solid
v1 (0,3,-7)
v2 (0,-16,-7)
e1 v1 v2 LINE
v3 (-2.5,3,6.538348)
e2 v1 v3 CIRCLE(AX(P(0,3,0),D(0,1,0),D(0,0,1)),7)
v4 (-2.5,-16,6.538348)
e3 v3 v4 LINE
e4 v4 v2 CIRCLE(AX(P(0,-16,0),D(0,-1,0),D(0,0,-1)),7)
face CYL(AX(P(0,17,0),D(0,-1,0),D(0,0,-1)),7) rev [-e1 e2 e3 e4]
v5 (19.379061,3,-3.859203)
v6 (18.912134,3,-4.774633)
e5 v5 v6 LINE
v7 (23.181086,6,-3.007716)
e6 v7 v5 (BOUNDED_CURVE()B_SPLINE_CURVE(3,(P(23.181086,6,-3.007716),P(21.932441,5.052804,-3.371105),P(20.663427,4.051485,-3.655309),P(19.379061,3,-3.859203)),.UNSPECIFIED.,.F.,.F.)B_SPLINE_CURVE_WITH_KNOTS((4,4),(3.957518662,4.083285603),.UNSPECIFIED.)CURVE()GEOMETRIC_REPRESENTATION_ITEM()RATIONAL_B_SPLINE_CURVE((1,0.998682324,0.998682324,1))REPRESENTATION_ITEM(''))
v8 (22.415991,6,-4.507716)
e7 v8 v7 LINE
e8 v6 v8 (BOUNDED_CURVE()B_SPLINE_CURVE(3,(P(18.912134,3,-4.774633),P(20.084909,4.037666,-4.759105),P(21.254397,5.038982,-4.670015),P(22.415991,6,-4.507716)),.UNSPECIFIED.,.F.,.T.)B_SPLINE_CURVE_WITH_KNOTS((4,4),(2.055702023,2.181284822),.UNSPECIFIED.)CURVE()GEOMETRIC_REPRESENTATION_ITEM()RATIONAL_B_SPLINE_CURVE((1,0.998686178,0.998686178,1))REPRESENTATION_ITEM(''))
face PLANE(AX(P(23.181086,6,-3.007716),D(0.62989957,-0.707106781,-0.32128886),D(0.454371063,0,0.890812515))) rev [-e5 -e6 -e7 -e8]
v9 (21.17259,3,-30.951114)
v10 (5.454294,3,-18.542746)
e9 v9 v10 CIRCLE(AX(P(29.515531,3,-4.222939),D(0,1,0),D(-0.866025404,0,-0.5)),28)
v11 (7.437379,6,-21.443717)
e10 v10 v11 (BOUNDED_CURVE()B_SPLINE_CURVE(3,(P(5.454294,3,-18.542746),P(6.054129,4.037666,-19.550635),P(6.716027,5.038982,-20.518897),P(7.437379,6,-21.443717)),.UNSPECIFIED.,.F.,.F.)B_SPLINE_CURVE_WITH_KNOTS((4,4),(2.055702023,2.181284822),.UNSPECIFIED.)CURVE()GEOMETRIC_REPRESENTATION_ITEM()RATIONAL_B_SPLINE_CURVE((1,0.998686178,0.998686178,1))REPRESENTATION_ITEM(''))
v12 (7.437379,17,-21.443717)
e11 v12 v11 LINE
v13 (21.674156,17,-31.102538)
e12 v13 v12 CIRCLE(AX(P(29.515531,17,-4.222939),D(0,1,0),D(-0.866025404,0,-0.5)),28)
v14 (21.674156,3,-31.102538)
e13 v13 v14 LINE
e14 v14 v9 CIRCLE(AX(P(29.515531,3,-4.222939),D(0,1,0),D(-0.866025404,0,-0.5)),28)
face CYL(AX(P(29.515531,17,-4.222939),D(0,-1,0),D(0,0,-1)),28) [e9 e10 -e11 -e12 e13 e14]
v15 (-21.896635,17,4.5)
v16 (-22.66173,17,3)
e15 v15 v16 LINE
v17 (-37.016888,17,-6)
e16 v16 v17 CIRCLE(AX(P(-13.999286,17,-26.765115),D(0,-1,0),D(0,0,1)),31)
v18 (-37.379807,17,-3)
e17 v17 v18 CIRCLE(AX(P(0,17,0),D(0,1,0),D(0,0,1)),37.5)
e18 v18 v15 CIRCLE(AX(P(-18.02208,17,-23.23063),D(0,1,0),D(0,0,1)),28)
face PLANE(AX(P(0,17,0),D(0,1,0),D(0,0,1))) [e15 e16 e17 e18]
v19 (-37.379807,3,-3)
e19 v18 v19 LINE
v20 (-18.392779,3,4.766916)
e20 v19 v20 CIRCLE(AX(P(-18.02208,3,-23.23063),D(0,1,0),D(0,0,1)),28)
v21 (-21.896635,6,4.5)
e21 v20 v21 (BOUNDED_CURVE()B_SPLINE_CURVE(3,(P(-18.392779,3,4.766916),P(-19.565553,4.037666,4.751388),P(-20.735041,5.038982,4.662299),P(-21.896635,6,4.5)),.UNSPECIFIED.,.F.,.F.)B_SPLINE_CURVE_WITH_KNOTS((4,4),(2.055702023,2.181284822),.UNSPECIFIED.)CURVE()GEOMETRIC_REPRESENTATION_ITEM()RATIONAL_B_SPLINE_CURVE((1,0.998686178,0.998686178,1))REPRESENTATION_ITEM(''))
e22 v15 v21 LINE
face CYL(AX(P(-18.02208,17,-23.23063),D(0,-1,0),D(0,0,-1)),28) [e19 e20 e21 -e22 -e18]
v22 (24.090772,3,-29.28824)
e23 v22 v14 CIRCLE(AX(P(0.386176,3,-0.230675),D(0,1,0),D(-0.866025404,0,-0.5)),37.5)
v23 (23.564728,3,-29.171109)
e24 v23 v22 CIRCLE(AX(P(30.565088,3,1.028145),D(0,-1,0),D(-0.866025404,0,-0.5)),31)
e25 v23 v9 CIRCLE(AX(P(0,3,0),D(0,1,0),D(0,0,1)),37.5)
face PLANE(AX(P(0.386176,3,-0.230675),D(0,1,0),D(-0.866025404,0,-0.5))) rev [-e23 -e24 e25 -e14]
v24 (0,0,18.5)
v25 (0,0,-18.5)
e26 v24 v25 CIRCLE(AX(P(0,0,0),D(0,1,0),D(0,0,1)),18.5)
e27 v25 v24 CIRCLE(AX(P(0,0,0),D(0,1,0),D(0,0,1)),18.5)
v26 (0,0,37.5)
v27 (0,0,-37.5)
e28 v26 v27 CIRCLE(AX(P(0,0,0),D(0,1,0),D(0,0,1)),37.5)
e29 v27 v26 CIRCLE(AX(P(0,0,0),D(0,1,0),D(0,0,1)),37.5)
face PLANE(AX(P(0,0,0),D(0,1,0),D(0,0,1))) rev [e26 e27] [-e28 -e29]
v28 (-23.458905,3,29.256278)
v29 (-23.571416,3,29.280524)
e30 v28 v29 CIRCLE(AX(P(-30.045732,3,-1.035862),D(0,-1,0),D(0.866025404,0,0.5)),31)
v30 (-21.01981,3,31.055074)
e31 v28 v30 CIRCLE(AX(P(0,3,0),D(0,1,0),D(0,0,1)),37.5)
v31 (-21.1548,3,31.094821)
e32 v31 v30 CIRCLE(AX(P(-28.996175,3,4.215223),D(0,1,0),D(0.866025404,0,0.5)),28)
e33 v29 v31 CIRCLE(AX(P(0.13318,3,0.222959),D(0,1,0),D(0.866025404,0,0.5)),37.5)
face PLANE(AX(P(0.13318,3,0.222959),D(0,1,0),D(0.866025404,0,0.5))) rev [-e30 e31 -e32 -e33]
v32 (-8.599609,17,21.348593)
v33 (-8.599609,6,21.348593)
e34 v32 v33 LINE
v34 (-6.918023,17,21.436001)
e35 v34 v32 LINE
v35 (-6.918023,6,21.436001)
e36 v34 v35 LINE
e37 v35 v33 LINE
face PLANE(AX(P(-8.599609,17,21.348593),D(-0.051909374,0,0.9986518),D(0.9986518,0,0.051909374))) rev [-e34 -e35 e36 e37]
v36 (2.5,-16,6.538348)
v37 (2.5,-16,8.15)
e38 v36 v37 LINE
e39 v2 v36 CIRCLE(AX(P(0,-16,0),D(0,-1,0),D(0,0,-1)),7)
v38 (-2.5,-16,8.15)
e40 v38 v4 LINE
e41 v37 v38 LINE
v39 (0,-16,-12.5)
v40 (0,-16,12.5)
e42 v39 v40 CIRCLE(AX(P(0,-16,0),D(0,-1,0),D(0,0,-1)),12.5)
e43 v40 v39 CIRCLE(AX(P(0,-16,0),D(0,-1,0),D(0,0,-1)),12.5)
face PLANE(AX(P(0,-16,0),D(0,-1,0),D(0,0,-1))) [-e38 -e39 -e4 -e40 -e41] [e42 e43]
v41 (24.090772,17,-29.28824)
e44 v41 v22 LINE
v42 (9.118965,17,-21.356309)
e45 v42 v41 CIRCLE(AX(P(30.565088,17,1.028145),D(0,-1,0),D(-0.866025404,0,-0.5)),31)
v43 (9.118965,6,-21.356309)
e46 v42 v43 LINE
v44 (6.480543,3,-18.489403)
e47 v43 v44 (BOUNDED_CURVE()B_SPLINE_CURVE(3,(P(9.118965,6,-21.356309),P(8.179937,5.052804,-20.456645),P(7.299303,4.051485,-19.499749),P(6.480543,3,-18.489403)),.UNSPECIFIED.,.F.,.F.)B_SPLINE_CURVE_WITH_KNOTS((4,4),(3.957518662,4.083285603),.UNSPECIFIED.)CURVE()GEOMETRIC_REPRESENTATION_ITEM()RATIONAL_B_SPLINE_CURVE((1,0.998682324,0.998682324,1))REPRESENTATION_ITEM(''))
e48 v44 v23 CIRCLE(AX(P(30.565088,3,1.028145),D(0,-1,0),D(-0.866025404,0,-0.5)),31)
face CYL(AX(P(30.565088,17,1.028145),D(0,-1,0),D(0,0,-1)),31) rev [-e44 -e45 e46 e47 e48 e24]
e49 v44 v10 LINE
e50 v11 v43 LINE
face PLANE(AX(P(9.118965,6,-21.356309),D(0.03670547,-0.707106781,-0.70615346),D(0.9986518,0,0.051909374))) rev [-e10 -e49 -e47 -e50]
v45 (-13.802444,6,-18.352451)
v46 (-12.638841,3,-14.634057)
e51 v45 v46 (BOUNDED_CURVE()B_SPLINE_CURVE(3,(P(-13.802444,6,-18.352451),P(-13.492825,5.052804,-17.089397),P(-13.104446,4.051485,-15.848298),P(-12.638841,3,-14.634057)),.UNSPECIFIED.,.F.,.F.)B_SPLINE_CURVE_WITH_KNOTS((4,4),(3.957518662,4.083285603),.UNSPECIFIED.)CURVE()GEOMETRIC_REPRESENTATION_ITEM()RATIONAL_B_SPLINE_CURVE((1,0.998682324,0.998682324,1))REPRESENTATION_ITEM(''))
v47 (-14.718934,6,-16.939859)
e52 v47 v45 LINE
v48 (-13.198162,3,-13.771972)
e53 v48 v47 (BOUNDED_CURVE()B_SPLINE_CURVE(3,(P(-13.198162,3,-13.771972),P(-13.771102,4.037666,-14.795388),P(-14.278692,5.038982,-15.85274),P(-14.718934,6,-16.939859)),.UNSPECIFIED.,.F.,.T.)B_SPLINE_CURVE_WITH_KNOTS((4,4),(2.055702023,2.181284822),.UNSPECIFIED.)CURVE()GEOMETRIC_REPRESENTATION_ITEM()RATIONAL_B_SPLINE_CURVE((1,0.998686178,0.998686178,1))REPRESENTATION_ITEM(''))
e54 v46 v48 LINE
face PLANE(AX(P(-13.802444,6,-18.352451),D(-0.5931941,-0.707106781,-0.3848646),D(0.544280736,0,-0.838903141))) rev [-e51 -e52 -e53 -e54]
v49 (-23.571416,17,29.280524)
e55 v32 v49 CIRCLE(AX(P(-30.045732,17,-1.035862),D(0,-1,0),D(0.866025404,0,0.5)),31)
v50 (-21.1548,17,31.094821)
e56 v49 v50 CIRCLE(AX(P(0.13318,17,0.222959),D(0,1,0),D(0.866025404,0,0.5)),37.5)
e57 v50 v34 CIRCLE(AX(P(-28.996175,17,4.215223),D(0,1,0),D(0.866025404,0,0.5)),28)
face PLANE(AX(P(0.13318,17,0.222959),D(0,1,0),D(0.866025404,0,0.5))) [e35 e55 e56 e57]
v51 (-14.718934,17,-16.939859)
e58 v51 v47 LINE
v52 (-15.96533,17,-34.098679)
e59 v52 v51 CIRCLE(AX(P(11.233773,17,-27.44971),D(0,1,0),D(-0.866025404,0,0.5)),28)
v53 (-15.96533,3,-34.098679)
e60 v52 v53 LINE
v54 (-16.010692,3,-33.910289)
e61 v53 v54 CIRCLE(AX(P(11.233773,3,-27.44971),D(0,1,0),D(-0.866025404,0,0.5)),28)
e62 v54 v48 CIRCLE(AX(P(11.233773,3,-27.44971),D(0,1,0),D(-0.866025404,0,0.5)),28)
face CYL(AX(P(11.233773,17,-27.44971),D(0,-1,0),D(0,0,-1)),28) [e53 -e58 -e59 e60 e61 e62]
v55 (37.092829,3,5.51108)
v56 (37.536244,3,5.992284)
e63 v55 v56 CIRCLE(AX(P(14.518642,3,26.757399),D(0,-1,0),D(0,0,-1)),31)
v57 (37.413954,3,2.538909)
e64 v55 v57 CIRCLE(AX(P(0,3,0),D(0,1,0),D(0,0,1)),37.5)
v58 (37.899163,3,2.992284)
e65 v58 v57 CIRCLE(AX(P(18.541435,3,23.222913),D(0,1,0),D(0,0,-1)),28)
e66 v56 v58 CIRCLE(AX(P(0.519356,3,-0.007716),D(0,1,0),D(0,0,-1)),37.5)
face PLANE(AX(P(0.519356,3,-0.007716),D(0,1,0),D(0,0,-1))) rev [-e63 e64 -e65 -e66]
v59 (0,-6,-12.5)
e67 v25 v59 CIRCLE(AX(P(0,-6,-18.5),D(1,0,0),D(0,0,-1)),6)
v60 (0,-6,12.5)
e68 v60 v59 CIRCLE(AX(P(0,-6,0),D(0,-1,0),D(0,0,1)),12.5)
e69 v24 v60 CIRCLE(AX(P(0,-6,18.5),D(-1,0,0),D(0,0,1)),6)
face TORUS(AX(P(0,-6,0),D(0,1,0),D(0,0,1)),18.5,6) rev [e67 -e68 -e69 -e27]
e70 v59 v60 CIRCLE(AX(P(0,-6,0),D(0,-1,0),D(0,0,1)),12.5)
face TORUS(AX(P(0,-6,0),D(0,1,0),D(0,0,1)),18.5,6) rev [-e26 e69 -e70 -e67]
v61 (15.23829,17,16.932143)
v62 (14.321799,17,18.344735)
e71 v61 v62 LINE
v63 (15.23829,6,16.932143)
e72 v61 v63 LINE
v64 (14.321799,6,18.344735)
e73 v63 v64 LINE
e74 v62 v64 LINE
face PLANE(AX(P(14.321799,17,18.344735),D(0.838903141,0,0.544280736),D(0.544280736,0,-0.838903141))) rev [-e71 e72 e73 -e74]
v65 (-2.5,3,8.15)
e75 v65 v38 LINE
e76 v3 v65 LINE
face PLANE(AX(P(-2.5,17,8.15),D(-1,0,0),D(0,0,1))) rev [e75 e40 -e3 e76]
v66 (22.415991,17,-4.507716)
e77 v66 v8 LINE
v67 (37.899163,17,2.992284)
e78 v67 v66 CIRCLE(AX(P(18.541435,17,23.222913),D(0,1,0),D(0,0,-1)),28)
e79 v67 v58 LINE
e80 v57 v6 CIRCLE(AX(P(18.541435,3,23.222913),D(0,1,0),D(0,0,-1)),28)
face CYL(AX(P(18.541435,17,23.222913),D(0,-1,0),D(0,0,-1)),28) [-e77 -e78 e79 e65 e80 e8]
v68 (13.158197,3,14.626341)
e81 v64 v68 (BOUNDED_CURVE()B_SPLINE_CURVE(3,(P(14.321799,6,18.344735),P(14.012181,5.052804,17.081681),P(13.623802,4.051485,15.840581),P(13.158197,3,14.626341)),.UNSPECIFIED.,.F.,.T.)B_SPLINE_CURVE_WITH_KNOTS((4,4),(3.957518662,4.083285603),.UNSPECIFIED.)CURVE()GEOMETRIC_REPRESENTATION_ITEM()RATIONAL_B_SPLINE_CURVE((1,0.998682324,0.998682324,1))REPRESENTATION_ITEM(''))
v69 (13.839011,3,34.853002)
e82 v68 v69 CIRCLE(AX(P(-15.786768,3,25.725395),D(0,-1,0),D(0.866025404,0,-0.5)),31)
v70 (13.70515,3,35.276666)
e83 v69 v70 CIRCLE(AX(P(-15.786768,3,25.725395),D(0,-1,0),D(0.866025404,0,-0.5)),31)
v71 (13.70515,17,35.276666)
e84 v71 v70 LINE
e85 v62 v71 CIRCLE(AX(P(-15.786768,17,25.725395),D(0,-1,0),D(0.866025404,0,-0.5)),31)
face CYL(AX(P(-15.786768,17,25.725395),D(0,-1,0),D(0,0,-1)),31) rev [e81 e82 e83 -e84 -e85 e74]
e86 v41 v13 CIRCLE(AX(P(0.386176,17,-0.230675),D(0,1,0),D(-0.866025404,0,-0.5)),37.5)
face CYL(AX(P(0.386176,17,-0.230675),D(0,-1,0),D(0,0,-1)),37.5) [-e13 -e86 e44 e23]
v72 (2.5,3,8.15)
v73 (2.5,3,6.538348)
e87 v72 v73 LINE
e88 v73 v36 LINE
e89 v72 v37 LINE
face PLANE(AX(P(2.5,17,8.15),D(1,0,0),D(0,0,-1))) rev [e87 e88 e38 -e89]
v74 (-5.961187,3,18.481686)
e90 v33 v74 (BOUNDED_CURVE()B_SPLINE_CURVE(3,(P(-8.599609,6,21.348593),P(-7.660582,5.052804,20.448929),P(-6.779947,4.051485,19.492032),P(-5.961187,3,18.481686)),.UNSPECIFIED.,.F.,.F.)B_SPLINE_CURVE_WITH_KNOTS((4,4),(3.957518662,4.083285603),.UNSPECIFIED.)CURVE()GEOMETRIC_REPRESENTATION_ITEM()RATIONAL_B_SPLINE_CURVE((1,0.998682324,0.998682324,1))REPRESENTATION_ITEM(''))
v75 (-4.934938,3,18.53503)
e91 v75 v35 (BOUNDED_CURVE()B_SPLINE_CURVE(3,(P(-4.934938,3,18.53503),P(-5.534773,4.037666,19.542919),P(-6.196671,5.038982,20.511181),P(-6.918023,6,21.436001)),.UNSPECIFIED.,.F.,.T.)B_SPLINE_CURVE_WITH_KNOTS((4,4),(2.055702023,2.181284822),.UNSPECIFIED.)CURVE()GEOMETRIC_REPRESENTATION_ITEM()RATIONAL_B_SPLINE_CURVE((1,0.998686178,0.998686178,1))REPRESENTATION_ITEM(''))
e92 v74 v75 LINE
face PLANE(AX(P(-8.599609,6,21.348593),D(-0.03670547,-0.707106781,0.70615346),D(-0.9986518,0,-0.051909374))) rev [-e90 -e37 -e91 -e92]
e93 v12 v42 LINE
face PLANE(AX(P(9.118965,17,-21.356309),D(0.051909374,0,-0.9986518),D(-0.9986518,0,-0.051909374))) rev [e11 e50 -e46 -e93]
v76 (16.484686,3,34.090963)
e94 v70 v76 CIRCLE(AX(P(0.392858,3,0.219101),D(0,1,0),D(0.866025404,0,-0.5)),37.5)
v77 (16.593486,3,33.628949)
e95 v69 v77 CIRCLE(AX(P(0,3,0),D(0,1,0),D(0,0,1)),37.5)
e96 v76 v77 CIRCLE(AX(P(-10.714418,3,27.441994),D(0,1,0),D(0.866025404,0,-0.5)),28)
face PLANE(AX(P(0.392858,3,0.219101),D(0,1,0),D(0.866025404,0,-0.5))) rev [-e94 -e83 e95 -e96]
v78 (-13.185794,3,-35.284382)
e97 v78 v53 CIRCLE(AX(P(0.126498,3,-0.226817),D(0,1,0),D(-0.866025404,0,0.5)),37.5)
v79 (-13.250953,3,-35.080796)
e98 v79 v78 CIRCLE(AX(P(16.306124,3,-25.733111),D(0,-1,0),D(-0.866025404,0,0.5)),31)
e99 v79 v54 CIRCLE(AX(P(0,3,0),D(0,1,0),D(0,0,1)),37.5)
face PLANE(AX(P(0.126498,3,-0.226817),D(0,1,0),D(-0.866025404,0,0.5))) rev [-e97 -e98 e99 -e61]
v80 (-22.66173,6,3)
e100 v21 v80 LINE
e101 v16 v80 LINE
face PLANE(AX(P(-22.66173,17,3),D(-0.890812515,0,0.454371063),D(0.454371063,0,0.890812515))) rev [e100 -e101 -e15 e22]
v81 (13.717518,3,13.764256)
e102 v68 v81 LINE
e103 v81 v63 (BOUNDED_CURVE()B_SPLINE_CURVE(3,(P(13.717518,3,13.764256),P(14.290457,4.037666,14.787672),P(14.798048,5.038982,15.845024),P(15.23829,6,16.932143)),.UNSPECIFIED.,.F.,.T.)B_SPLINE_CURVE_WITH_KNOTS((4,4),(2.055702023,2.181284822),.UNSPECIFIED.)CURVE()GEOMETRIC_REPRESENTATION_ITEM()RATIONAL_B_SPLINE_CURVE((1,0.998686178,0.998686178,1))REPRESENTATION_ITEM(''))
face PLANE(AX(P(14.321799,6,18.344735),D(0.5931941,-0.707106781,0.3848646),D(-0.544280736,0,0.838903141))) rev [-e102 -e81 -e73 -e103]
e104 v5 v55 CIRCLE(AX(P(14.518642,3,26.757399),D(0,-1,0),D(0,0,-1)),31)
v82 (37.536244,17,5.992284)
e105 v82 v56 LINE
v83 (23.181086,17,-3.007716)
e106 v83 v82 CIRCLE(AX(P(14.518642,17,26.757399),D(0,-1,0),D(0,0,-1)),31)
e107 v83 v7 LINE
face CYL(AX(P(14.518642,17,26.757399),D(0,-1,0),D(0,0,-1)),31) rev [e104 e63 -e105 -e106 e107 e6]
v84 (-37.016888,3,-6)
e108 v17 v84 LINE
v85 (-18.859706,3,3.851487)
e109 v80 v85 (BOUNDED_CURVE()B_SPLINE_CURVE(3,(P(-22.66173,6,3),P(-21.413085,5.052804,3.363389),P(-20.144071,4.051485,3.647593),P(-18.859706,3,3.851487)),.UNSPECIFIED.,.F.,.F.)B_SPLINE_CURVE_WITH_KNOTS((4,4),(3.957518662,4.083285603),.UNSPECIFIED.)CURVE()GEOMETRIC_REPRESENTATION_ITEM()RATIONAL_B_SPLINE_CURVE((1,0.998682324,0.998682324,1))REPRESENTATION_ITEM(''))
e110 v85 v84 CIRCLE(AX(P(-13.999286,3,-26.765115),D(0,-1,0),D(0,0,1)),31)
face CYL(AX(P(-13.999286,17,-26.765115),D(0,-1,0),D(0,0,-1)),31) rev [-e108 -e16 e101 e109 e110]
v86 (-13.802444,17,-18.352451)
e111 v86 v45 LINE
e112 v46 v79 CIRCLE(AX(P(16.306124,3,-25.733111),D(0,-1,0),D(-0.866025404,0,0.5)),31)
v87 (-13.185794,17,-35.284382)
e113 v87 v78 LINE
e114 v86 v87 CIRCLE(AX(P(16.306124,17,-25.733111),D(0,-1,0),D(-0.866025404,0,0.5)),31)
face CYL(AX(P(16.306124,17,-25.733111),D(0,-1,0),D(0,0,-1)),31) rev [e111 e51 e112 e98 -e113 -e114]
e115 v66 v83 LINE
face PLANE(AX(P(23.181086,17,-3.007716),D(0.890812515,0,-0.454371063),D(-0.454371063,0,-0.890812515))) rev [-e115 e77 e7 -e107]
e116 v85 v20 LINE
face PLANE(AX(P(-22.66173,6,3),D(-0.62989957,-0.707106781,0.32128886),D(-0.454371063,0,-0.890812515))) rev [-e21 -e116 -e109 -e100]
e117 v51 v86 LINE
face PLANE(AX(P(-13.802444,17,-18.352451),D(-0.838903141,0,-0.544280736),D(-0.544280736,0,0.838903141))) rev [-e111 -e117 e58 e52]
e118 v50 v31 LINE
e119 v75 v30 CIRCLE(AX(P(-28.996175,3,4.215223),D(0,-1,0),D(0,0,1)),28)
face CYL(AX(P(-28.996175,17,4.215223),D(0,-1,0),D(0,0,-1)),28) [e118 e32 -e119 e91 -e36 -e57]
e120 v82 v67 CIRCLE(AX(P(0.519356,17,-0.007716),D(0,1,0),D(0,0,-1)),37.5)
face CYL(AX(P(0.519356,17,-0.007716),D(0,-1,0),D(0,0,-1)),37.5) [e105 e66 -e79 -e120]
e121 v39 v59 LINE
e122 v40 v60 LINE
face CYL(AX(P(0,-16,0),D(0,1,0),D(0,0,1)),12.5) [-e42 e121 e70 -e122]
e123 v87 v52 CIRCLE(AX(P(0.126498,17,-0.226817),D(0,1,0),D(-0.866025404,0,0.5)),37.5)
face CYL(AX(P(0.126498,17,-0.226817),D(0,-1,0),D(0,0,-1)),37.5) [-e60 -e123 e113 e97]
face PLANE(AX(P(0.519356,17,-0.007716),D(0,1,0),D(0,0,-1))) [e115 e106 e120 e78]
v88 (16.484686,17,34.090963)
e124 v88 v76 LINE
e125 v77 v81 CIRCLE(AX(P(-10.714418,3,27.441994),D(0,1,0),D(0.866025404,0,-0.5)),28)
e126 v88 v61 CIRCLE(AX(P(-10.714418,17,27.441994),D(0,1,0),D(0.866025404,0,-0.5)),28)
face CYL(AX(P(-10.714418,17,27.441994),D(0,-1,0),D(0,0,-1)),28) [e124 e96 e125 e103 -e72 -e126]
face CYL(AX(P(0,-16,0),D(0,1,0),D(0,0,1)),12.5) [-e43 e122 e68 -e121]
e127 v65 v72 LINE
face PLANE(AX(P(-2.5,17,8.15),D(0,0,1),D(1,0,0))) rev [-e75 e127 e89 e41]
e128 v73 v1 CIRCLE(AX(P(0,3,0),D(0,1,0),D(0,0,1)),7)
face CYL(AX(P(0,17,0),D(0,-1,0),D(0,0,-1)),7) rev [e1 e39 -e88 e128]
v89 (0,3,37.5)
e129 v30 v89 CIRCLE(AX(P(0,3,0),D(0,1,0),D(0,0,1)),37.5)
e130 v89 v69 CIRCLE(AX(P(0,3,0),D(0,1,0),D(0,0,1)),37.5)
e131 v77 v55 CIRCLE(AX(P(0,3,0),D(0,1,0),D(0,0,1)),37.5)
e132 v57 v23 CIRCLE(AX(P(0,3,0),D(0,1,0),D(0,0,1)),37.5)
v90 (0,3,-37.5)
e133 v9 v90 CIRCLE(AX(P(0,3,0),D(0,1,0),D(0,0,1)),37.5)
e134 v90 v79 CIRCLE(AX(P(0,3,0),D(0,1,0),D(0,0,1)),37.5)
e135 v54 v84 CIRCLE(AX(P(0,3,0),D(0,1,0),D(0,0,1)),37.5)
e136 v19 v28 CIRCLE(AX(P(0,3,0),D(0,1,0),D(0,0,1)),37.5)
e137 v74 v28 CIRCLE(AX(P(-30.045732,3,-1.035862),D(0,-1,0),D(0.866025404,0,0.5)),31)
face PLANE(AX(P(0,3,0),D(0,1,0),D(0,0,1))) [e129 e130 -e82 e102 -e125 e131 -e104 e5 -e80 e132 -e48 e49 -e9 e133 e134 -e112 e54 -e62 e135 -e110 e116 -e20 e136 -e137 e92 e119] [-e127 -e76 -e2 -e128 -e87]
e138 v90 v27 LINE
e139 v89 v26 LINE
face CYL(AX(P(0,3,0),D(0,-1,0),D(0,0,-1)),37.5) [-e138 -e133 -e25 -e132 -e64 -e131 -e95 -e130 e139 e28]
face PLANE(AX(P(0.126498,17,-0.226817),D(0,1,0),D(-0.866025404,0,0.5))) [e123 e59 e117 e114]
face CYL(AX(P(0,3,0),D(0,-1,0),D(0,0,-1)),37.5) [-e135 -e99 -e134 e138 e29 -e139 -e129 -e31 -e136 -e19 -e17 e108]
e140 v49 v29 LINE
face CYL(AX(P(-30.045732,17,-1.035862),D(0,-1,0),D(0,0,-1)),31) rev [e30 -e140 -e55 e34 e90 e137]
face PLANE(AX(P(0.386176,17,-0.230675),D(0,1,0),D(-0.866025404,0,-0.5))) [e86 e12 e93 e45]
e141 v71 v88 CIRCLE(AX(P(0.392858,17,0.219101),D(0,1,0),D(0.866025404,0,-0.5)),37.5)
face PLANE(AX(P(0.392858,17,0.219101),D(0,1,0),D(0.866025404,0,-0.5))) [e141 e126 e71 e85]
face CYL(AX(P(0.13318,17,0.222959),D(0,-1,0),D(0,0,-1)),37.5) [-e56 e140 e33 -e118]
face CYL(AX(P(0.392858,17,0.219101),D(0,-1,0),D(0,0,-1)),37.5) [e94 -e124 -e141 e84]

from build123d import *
from build123d.topology import SkipClean

# Parameters (mm, degrees)
BASE_DISC_SKETCH_R                         = 37.5
BASE_DISC_75_DEPTH                         = 3
VANE_DEPTH                                 = 14
VANE_CHAMFER_3MM_SIZE                      = 3
VANE_PATTERN_6X60_COUNT                    = 6
VANE_CHAMFER_3MM_OF_VANE_PATTERN_6X60_SIZE = 3
HUB_SKETCH_R                               = 12.5
HUB_25_DEPTH                               = 16
SHAFT_BORE_14_DEPTH                        = 63.702444686
SHAFT_BORE_14_DEPTH_BACK                   = 63.702444686
HUB_FILLET_R6_R                            = 6


with BuildPart() as part:
    # Base Disc Sketch → Base Disc Ø75 (new body)
    with BuildSketch(Plane(origin=(0, 0, 0), x_dir=(1, 0, 0), z_dir=(0, 1, 0))):
        with Locations(Location((0, 0, 0), (0, 0, 270))):
            Circle(BASE_DISC_SKETCH_R)
    extrude(amount=BASE_DISC_75_DEPTH)

    # Vane Profile Sketch → Vane (add)
    with SkipClean():  # the faces are left unmerged after this step: merging them gives an invalid solid
        with BuildSketch(Plane(origin=(0, 3, 0), x_dir=(1, 0, 0), z_dir=(0, 1, 0))):
            with BuildLine():
                Line((-22.661730354, -3), (-21.896634912, -4.5))
                ThreePointArc((-21.896634912, -4.5), (-30.228522345, -1.968631367), (-37.379807383, 3))
                ThreePointArc((-37.379807383, 3), (-37.228578705, 4.503657138), (-37.016888038, 6))
                ThreePointArc((-37.016888038, 6), (-30.466111276, 0.5002397), (-22.661730354, -3))
            make_face()
        vane = extrude(amount=VANE_DEPTH)

    # Vane Chamfer 3mm
    vane_chamfer_3mm_edges = [part.edges().sort_by_distance(p)[0] for p in [
        (-22.279182633, 3, 3.75),
    ]]
    chamfer(vane_chamfer_3mm_edges, length=VANE_CHAMFER_3MM_SIZE)

    # Vane Pattern 6x60°: Vane ×6 about axis
    with SkipClean():  # the faces are left unmerged after this step: merging them gives an invalid solid
        vane_pattern_6x60_axis = Axis((0.259677898, 0, -0.003858097), (0, 1, 0))
        for i in range(1, VANE_PATTERN_6X60_COUNT):
            add(vane.rotate(vane_pattern_6x60_axis, i * 360 / VANE_PATTERN_6X60_COUNT))

    # Vane Chamfer 3mm of Vane Pattern 6x60°
    vane_chamfer_3mm_of_vane_pattern_6x60_edges = [part.edges().sort_by_distance(p)[0] for p in [
        (-7.758815893, 3, 21.392296743),
        (14.780044637, 3, 17.638438646),
        (22.798538428, 3, -3.757716194),
        (8.278171688, 3, -21.400012937),
        (-14.260688842, 3, -17.64615484),
    ]]
    chamfer(vane_chamfer_3mm_of_vane_pattern_6x60_edges, length=VANE_CHAMFER_3MM_OF_VANE_PATTERN_6X60_SIZE)

    # Hub Sketch → Hub Ø25 (add)
    with SkipClean():  # the faces are left unmerged after this step: merging them gives an invalid solid
        with BuildSketch(Plane.XZ):
            with Locations(Location((0, 0, 0), (0, 0, 270))):
                Circle(HUB_SKETCH_R)
        extrude(amount=HUB_25_DEPTH)

    # Shaft Bore Sketch → Shaft Bore Ø14 (cut, two sides: drawn at the far end of the back side and taken through both)
    with SkipClean():  # the faces are left unmerged after this step: merging them gives an invalid solid
        with BuildSketch(Plane.XZ.offset(16).offset(-SHAFT_BORE_14_DEPTH_BACK)):
            with BuildLine():
                Line((-2.5, 8.15), (2.5, 8.15))
                Line((2.5, 8.15), (2.5, 6.538348415))
                ThreePointArc((2.5, 6.538348415), (0, -7), (-2.5, 6.538348415))
                Line((-2.5, 6.538348415), (-2.5, 8.15))
            make_face()
        extrude(amount=SHAFT_BORE_14_DEPTH + SHAFT_BORE_14_DEPTH_BACK, mode=Mode.SUBTRACT)

    # Hub Fillet R6
    hub_fillet_r6_edges = [part.edges().sort_by_distance(p)[0] for p in [
        (0, 0, 12.5),
    ]]
    fillet(hub_fillet_r6_edges, radius=HUB_FILLET_R6_R)


solid = part.part
